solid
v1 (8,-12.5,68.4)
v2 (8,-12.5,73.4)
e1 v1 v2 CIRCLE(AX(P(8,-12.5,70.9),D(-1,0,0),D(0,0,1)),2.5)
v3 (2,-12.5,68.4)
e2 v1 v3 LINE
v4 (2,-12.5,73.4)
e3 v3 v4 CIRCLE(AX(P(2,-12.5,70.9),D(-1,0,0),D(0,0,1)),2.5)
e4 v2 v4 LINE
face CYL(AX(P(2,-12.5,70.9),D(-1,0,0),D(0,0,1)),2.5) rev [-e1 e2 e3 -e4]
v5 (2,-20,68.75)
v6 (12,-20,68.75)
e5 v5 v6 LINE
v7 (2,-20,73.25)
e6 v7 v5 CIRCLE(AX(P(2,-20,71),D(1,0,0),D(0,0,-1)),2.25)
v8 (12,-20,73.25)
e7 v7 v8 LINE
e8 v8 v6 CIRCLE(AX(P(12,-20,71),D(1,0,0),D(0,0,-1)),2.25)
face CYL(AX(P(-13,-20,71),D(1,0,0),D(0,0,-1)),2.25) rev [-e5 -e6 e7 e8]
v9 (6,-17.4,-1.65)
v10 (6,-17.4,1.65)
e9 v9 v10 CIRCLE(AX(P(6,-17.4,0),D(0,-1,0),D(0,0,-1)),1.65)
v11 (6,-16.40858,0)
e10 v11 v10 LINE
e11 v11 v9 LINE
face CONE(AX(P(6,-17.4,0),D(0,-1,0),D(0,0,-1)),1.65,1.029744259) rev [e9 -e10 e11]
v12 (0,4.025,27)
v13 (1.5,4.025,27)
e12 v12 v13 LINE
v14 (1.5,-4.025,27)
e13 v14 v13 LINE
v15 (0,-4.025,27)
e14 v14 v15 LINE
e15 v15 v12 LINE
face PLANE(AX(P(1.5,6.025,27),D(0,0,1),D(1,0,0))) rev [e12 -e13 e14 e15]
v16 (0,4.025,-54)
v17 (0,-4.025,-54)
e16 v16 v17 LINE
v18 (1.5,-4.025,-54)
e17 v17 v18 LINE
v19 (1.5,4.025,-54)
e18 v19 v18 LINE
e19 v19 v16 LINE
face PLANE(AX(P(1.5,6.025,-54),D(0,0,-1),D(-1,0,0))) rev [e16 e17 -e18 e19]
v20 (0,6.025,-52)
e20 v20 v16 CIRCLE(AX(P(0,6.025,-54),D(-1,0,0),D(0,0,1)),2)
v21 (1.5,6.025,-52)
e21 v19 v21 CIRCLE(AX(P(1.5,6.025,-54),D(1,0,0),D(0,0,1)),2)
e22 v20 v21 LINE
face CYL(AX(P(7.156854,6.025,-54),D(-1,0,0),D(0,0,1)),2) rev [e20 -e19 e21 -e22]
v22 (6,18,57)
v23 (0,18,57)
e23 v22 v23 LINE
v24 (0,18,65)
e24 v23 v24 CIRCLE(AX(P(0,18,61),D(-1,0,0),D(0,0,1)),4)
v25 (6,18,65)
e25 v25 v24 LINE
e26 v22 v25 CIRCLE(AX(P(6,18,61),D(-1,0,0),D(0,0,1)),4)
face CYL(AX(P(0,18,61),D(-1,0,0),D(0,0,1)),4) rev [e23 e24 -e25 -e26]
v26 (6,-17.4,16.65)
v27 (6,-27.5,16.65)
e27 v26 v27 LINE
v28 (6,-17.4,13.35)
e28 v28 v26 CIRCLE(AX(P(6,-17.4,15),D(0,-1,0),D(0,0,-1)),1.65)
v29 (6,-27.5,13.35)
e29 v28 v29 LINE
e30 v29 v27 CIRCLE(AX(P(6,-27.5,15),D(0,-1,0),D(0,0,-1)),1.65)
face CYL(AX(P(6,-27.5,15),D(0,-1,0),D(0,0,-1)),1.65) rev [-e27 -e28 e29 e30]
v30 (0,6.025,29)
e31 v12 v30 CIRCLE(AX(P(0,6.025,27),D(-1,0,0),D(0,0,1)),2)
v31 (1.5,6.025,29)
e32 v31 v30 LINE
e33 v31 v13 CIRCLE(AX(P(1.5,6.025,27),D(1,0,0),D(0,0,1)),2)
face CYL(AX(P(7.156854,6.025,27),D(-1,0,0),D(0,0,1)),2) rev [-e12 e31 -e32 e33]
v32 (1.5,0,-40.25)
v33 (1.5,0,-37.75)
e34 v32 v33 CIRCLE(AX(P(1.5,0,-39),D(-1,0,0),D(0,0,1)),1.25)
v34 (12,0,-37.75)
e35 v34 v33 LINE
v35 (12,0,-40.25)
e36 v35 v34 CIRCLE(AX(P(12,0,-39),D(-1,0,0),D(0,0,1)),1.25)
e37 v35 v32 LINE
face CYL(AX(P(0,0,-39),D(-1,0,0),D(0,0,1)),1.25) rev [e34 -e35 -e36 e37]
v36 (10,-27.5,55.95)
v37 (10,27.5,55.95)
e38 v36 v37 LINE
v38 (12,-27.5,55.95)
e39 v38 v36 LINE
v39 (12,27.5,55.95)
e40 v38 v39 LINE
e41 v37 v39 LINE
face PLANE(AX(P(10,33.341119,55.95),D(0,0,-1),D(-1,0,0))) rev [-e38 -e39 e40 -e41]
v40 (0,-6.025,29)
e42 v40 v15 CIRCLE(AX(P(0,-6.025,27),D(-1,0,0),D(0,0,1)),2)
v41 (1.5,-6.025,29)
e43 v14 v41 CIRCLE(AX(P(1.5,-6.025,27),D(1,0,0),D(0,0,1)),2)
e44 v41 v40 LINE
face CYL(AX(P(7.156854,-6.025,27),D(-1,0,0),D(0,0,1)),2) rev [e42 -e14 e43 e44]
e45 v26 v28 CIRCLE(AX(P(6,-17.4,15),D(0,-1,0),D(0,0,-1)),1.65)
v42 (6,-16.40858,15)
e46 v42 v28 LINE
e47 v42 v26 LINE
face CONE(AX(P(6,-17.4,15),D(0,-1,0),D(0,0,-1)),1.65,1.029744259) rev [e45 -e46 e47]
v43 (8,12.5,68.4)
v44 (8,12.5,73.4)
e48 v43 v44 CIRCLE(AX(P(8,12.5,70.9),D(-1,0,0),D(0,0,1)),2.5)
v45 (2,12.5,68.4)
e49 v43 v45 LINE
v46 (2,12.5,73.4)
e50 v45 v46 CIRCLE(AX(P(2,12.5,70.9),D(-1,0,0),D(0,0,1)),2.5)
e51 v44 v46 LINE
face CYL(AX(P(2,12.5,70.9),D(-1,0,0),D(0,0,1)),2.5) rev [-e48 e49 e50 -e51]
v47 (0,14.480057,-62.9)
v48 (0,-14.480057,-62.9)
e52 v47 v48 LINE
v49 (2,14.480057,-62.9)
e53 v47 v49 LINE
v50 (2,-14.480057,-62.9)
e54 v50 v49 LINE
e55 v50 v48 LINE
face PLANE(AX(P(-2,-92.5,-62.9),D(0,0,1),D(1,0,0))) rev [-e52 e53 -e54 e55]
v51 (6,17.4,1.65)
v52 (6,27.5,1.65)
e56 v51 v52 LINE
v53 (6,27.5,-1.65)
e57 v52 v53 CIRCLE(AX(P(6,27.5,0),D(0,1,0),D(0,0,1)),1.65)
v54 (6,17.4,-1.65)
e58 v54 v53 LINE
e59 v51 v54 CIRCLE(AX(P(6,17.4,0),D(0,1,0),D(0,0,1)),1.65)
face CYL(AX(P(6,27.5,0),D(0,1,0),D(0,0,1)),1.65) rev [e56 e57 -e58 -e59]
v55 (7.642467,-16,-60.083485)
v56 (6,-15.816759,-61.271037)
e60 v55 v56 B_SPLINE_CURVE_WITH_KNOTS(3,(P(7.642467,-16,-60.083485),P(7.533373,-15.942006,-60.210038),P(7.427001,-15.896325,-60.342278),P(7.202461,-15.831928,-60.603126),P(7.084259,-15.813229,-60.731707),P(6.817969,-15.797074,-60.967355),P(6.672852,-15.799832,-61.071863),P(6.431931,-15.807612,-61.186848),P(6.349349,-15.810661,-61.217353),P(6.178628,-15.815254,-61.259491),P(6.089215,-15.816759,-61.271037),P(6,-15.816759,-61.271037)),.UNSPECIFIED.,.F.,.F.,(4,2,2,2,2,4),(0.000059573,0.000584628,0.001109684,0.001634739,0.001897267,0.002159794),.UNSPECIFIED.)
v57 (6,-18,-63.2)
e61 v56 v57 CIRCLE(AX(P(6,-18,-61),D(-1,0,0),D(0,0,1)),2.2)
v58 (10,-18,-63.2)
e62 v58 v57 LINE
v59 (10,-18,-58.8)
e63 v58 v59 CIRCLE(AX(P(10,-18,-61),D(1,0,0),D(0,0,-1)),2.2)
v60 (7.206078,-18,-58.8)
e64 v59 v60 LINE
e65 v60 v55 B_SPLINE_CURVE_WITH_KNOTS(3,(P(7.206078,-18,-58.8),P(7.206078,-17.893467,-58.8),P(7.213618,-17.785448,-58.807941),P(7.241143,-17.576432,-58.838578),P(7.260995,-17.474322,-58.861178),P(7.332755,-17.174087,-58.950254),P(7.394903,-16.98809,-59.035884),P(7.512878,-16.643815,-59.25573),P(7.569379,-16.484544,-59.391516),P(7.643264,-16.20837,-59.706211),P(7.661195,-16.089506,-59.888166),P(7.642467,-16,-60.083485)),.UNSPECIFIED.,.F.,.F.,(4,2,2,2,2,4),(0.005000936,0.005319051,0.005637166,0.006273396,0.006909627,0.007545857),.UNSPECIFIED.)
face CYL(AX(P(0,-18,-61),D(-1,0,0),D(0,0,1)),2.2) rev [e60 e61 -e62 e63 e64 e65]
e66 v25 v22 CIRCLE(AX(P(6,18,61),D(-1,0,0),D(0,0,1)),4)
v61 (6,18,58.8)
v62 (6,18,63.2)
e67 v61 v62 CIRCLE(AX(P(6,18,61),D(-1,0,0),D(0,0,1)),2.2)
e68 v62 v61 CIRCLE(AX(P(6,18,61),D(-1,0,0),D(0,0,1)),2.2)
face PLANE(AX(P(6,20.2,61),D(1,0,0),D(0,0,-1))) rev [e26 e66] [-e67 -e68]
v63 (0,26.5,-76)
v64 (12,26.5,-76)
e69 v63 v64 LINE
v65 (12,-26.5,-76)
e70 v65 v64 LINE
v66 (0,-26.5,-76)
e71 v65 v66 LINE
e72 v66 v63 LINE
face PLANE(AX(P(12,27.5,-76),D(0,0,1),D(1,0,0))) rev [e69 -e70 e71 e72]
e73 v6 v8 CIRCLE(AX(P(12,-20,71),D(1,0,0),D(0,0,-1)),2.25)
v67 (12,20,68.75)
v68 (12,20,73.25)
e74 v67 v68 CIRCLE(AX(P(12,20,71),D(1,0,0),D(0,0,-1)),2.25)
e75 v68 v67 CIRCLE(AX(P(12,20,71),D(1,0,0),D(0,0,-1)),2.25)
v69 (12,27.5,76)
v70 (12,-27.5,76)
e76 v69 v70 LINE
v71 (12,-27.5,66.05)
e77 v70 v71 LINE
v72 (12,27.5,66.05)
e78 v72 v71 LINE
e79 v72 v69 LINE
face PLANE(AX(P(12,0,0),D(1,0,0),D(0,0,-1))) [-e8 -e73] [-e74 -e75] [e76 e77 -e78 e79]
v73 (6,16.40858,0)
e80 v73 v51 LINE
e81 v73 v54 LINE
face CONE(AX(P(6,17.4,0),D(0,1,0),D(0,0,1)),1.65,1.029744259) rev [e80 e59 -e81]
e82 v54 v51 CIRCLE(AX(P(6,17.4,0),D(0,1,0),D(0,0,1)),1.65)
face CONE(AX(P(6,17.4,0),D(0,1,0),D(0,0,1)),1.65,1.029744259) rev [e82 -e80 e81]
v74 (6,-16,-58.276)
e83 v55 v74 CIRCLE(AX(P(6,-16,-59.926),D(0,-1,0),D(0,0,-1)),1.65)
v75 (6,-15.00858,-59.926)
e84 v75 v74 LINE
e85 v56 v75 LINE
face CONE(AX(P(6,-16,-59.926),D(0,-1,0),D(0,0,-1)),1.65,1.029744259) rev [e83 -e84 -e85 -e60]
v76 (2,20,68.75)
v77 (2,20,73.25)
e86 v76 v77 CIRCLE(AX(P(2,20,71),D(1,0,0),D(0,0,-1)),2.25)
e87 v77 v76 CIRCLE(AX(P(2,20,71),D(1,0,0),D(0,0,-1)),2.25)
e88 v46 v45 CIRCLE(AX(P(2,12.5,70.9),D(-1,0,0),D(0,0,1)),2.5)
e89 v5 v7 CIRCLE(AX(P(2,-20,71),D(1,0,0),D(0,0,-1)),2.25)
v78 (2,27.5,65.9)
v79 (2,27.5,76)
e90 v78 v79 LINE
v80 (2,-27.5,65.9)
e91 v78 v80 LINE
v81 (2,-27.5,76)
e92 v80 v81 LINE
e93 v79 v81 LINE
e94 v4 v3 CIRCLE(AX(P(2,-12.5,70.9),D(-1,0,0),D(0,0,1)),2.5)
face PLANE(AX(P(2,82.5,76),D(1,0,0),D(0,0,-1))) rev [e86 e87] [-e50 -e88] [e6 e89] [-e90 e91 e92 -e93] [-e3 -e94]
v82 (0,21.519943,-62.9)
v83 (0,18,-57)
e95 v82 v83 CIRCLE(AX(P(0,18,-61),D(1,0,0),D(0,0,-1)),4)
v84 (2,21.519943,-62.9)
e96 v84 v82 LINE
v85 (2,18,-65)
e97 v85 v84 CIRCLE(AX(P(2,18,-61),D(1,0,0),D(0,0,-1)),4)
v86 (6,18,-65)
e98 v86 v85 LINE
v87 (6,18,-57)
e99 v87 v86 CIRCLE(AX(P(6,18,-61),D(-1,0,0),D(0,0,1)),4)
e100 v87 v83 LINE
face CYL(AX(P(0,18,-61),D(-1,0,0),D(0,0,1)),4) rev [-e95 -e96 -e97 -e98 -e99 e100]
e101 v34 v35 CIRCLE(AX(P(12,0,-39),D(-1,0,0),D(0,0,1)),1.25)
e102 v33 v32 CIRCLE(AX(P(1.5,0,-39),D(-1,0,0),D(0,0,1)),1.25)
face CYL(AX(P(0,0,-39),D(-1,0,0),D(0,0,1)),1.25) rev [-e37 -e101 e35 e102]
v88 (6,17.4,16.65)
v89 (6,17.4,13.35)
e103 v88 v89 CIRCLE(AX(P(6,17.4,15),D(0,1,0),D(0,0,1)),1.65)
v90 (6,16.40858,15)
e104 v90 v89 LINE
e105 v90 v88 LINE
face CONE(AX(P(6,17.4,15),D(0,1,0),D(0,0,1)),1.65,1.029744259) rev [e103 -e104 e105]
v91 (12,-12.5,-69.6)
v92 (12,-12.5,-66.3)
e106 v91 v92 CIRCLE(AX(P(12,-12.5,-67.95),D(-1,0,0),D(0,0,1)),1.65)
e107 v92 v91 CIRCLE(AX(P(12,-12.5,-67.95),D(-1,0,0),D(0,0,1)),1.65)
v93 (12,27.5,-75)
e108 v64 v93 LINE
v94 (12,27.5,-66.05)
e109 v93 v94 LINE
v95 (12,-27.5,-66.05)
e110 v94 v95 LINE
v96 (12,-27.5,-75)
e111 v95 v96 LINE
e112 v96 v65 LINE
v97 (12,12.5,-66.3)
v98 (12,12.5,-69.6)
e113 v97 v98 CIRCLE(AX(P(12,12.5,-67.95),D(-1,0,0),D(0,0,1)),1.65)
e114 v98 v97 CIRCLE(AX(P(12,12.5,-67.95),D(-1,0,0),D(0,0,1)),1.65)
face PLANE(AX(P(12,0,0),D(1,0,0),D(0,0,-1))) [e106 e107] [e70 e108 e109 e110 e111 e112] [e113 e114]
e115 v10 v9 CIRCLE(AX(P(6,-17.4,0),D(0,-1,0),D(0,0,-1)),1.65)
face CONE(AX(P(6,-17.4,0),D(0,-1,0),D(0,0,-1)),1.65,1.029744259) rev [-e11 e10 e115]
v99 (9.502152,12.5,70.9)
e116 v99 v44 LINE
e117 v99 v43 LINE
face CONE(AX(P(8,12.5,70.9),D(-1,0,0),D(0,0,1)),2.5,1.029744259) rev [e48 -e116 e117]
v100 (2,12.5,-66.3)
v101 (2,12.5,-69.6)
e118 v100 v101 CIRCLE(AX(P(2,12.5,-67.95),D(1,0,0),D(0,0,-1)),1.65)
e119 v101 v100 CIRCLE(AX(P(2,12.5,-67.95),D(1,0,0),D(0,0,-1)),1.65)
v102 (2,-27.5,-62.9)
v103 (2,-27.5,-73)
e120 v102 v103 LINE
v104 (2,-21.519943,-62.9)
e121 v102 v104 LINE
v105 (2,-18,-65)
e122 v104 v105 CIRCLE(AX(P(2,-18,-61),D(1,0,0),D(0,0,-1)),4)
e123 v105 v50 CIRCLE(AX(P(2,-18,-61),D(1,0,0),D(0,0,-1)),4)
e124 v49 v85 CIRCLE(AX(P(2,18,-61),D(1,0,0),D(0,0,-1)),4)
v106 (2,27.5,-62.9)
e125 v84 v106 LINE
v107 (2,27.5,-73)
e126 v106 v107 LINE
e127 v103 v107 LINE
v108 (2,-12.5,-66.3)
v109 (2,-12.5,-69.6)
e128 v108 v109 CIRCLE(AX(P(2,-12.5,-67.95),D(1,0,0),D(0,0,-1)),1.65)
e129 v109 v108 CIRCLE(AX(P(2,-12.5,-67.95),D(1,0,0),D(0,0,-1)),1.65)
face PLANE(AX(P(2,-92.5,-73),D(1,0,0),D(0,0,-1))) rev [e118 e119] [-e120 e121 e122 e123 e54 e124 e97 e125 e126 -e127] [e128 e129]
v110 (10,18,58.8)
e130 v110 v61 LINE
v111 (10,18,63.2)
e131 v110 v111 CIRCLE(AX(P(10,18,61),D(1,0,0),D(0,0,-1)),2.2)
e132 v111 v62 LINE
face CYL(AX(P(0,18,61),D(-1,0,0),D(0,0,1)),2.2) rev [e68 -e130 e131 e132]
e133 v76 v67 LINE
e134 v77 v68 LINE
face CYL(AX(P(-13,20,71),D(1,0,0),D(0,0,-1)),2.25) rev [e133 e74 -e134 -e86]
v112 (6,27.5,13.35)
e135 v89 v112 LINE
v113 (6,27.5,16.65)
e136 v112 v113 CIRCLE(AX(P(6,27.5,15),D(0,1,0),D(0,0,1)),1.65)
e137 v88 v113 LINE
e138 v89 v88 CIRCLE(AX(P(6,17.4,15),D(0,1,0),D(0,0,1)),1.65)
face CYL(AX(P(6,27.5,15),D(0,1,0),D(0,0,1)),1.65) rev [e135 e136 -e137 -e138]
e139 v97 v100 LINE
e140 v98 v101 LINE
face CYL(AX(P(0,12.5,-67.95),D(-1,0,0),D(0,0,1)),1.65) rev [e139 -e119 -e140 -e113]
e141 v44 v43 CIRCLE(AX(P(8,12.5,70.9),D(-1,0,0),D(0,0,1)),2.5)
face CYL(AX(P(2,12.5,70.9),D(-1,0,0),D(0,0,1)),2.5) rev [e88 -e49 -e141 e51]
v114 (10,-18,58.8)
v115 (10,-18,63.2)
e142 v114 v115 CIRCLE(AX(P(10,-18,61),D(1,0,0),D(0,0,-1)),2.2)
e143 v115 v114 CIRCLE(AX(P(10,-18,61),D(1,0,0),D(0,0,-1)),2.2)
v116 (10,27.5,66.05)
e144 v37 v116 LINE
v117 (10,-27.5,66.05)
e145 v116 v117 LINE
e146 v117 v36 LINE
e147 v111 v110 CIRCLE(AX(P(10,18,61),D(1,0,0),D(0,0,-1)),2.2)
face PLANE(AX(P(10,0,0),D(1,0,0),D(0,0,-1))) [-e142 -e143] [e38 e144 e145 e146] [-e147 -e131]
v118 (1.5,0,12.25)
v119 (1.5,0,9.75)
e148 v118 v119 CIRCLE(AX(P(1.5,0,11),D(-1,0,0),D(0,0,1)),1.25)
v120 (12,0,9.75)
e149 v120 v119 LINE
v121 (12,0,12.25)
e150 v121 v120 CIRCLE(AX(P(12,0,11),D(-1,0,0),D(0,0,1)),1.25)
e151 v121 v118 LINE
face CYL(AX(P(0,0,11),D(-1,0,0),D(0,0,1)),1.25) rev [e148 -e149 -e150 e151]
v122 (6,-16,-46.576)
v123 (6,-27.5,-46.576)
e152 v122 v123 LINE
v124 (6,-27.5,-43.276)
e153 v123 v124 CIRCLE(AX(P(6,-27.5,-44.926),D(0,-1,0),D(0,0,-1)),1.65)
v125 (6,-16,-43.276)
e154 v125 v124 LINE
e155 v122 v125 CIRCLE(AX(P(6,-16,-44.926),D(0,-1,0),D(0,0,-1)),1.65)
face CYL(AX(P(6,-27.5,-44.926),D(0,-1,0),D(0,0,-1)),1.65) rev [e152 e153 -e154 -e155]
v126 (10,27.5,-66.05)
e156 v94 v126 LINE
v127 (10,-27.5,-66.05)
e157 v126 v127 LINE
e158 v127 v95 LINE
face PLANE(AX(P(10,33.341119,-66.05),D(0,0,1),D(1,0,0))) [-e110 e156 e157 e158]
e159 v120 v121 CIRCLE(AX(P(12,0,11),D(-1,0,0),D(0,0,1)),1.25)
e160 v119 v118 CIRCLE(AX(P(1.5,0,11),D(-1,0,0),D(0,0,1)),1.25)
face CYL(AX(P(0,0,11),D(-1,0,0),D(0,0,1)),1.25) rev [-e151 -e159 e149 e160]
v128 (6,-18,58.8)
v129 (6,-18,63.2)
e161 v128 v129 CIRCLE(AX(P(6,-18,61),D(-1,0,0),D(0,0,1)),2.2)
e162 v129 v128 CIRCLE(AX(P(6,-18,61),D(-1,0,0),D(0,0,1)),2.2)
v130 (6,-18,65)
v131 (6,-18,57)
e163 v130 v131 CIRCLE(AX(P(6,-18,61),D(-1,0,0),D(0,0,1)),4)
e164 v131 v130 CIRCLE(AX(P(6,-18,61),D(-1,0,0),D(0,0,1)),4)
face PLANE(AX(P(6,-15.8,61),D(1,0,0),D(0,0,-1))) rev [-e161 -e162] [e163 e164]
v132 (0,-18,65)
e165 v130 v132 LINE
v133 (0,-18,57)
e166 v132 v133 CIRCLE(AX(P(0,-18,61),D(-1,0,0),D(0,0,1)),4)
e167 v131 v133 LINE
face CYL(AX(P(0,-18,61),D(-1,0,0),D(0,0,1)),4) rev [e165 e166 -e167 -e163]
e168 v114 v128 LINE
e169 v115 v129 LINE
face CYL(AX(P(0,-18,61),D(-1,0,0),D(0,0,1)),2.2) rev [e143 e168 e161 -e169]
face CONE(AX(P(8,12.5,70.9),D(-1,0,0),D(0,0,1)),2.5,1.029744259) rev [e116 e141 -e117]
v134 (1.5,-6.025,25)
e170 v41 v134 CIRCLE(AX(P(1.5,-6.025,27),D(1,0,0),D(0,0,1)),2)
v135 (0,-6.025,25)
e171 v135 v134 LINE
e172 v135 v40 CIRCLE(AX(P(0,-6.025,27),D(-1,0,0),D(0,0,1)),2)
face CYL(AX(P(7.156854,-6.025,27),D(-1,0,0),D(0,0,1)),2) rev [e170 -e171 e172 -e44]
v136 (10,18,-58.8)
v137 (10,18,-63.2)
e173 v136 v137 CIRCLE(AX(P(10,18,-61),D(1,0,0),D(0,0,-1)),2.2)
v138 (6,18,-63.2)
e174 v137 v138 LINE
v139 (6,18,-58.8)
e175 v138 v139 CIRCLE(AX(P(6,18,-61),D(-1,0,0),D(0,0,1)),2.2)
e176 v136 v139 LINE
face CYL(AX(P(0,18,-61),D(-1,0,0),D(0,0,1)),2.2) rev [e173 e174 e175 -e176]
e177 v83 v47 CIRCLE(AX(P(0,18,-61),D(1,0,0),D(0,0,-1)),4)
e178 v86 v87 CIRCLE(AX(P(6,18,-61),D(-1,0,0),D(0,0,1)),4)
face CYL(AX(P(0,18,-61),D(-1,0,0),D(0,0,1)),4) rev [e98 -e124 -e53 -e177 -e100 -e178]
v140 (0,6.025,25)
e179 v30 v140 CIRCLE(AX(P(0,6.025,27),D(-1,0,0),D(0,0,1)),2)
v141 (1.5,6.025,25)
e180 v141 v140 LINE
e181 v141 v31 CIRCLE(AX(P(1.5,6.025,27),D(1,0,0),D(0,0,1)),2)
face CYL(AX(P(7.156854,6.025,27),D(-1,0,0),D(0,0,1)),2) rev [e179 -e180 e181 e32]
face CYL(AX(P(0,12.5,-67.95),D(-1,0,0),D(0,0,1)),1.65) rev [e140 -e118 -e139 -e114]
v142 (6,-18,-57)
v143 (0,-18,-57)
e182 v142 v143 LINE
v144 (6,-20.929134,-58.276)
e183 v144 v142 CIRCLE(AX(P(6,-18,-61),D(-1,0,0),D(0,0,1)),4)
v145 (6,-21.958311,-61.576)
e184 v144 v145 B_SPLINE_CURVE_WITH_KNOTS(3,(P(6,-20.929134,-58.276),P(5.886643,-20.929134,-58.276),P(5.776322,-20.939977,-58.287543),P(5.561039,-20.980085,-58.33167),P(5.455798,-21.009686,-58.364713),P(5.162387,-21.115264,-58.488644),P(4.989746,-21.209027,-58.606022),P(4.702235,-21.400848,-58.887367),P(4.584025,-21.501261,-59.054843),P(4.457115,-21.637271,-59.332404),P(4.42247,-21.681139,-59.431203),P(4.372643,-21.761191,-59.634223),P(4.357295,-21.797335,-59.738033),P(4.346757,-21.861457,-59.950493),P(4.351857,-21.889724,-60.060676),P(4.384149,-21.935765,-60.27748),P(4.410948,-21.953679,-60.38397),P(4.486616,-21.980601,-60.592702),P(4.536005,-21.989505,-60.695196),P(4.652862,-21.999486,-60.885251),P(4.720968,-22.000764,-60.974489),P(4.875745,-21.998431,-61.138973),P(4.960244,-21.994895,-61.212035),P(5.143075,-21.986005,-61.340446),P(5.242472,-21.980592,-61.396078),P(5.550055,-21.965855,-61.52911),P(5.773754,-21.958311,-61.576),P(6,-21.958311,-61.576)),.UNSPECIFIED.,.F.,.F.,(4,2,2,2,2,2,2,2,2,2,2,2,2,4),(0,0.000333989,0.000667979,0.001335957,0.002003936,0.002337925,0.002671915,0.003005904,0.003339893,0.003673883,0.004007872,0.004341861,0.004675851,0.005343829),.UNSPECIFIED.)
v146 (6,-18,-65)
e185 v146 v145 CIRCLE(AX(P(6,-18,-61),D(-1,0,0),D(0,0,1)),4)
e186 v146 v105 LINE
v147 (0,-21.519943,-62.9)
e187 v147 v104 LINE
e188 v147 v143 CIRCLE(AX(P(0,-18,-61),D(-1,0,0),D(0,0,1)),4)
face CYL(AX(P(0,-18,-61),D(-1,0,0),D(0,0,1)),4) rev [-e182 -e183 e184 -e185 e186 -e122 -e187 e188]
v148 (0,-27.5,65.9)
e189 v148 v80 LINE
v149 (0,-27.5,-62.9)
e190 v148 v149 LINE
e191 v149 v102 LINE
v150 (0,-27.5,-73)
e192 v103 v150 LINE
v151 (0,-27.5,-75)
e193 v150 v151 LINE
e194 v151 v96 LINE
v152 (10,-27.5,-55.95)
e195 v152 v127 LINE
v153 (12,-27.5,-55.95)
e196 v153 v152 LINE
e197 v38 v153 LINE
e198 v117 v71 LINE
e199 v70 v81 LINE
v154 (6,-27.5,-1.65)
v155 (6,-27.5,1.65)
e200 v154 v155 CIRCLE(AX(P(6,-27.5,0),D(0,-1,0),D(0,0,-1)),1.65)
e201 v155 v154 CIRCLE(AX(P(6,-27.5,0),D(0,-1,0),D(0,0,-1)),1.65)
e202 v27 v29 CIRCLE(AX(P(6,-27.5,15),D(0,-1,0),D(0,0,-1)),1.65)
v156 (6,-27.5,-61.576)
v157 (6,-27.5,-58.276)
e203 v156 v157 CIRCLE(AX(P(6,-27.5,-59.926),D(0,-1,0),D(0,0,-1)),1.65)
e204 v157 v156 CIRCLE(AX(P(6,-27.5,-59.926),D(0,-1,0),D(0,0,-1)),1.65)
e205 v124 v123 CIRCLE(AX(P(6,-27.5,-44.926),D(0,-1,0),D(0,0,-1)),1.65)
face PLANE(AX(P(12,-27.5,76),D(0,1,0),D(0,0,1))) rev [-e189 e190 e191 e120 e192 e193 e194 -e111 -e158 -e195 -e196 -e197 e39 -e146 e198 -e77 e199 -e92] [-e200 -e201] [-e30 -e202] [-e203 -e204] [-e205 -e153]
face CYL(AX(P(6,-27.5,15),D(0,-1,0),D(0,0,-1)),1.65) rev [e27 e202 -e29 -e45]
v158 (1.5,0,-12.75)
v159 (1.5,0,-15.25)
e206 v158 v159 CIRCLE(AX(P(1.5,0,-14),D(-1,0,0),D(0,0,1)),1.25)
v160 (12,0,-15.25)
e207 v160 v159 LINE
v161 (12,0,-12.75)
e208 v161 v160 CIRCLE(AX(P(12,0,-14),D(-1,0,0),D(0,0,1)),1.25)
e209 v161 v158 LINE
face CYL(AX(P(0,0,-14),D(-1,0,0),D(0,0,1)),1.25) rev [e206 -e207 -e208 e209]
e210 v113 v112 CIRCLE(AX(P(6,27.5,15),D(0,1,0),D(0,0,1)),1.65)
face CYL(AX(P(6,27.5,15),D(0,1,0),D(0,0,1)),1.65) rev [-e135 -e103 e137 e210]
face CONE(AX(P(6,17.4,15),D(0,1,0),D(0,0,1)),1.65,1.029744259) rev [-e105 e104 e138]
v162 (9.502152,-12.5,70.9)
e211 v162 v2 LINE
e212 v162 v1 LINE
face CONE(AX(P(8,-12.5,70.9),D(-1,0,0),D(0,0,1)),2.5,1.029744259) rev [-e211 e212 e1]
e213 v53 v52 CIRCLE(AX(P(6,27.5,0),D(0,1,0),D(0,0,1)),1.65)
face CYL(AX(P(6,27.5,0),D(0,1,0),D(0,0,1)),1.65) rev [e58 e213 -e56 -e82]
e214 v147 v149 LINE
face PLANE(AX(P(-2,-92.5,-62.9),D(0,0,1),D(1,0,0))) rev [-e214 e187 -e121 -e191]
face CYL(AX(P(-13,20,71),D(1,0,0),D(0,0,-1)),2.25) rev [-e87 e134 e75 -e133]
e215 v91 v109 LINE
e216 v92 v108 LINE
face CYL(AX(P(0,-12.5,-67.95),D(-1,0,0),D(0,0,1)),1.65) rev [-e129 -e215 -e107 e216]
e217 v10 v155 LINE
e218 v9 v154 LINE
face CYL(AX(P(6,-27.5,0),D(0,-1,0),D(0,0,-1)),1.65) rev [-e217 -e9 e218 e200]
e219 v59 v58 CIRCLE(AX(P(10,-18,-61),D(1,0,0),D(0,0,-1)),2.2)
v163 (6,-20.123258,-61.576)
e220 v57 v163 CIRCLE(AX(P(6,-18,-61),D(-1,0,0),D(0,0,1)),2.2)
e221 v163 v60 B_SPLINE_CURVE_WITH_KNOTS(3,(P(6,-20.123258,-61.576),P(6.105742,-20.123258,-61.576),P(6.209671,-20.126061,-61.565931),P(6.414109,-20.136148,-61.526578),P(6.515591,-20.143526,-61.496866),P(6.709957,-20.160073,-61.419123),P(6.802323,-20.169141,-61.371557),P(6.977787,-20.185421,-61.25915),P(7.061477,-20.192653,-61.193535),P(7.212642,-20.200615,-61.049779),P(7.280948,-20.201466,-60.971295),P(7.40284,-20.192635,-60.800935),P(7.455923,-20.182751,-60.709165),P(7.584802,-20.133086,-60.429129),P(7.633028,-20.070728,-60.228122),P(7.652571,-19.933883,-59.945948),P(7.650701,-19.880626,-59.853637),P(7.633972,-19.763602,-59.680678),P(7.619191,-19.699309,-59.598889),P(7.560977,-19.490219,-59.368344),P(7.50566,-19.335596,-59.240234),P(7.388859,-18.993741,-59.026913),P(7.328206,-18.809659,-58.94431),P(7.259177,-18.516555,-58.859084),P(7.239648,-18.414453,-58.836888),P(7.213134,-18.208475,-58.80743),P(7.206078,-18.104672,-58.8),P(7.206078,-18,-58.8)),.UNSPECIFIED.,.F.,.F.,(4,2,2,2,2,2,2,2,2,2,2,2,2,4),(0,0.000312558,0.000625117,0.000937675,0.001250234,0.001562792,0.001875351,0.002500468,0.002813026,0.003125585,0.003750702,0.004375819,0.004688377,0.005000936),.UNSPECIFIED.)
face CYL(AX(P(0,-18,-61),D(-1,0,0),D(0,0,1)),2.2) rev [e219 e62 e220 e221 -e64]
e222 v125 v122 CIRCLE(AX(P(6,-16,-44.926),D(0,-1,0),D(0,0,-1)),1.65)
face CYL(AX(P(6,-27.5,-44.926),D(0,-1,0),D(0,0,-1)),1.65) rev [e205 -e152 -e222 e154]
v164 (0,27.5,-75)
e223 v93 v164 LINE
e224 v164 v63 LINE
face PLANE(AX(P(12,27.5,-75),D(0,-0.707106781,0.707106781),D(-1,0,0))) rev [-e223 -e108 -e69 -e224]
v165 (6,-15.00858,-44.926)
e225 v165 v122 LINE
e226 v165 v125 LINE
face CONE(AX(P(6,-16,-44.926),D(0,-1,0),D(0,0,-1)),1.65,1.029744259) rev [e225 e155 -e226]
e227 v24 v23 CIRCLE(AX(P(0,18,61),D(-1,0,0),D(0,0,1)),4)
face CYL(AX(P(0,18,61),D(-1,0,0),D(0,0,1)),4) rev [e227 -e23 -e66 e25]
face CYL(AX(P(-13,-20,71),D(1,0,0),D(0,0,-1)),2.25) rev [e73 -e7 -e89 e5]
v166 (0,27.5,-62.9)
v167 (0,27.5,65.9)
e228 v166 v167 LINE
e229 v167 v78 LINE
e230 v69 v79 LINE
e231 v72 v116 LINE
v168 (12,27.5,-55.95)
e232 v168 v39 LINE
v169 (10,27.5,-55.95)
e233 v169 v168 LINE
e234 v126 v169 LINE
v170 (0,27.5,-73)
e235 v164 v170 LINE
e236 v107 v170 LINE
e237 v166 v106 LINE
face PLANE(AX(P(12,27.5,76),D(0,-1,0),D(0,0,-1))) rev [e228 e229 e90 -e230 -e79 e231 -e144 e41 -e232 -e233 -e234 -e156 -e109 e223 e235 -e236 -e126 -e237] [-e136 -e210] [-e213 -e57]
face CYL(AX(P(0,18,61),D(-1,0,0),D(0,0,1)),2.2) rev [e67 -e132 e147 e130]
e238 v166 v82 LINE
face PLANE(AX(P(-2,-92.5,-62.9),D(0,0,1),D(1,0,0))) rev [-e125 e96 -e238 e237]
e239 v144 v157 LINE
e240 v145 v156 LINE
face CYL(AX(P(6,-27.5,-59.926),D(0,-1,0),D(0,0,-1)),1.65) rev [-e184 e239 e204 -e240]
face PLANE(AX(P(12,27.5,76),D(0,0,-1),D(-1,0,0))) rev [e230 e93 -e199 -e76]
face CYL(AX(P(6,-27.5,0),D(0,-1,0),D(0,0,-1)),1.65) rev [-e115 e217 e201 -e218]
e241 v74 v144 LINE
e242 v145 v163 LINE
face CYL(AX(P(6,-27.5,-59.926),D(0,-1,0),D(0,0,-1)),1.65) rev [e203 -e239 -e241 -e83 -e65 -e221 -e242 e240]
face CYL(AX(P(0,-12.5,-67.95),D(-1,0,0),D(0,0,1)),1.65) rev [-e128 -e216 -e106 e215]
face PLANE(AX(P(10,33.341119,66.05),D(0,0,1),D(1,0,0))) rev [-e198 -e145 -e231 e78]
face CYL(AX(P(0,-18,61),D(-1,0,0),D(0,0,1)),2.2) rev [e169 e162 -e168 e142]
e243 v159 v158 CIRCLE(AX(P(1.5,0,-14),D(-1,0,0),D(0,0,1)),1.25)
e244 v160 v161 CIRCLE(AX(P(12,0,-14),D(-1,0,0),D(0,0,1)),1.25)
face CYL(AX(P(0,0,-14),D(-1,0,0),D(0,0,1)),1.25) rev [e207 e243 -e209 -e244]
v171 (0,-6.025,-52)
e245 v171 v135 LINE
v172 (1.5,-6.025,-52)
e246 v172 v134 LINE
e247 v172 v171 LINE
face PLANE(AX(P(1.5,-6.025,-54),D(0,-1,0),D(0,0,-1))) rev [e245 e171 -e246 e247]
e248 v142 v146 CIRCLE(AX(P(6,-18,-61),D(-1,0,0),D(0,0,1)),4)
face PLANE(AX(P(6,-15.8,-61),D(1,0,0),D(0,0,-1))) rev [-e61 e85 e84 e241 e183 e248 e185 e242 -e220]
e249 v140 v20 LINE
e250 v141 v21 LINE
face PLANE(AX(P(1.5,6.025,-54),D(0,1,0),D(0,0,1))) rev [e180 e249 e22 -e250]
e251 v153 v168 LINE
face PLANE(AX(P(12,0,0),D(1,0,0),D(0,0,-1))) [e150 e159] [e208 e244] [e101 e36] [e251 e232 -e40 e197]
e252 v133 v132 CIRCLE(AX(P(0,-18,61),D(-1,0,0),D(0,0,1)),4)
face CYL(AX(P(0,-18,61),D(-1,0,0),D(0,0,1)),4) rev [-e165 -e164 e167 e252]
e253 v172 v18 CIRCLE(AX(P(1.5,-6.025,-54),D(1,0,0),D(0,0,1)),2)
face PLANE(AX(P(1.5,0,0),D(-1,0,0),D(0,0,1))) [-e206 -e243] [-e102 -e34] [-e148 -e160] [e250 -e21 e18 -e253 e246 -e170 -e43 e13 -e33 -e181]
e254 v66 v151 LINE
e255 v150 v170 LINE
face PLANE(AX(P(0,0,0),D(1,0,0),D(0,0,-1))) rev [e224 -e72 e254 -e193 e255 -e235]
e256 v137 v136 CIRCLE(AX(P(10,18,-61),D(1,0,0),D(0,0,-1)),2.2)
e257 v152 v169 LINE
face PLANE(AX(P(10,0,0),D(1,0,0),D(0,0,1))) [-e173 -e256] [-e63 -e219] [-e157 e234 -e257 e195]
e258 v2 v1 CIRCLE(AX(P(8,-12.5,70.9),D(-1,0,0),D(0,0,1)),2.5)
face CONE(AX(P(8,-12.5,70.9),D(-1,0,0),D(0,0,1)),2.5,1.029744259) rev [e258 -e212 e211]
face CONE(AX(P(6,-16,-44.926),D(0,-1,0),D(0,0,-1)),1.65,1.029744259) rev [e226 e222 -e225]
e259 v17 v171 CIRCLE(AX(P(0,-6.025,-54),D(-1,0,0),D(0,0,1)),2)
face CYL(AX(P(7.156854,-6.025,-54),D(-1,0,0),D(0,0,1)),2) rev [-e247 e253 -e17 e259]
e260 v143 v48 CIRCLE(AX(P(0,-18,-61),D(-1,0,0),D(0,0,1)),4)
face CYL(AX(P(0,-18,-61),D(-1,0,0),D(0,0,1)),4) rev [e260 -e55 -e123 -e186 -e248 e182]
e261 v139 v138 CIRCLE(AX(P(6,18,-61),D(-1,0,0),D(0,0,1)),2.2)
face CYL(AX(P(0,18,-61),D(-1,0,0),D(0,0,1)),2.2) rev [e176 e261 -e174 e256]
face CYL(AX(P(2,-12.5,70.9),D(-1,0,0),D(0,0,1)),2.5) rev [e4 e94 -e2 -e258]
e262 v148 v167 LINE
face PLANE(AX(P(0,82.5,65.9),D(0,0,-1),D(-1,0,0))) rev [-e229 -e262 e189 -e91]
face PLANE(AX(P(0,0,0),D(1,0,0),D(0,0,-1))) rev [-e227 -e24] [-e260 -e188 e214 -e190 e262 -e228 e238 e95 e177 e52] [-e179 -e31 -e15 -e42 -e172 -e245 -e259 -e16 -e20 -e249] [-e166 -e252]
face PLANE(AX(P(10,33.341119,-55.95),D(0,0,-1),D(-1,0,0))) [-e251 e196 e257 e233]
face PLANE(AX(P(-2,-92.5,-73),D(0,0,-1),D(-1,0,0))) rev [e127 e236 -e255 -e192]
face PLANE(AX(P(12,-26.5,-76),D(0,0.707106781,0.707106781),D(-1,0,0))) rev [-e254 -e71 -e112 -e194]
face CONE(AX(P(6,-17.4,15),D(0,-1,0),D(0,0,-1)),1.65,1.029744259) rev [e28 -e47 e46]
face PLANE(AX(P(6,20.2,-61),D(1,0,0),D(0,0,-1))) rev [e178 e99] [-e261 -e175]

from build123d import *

# Parameters (mm, degrees)
SKETCH_1_W                  = 152
SKETCH_1_H                  = 55
EXTRUDE_1_DEPTH             = 12
SKETCH_2_W                  = 10.1
SKETCH_2_H                  = 67.741828953
CUT_EXTRUDE_1_DEPTH         = 2
SKETCH_3_W                  = 81
SKETCH_3_H                  = 12.05
CUT_EXTRUDE_2_DEPTH         = 1.5
SKETCH_4_R                  = 2
CUT_EXTRUDE_3_DEPTH         = 1.5
SKETCH_5_W                  = 2
SKETCH_5_H                  = 10.1
CUT_EXTRUDE_4_DEPTH         = 110
SKETCH_7_W                  = 4
SKETCH_7_H                  = 10.1
CUT_EXTRUDE_5_DEPTH         = 120
CHAMFER_1_SIZE              = 1
HOLE_WIZARD_M4_1_AT_2_COUNT = 2
HOLE_WIZARD_M4_1_AT_2_PITCH = 15
HOLE_WIZARD_5_0_5_2_D       = 5
HOLE_WIZARD_5_0_5_2_DEPTH   = 6
HOLE_WIZARD_5_0_5_2_TIP     = 1.502151548
HOLE_WIZARD_1_D             = 4.4
HOLE_WIZARD_1_CBORE_D       = 8
HOLE_WIZARD_1_CBORE_DEPTH   = 6
HOLE_WIZARD_M3_1_D          = 2.5
HOLE_WIZARD_M4_2_D          = 3.3
HOLE_WIZARD_M4_2_DEPTH      = 11.5
HOLE_WIZARD_M4_2_TIP        = 0.991420021
HOLE_WIZARD_M4_3_D          = 3.3
SKETCH_30_R                 = 2.25
CUT_EXTRUDE_6_DEPTH         = 25


with BuildPart() as part:
    # 草图1 → 凸台-拉伸1 (new body)
    with BuildSketch(Plane(origin=(0, 0, 0), x_dir=(0, 0, -1), z_dir=(1, 0, 0))):
        Rectangle(SKETCH_1_W, SKETCH_1_H)
    extrude(amount=EXTRUDE_1_DEPTH)

    # 草图2 → 切除-拉伸1 (cut)
    with BuildSketch(Plane(origin=(12, 0, 0), x_dir=(0, 0, -1), z_dir=(1, 0, 0))):
        with Locations((-61, -0.529795054)):
            Rectangle(SKETCH_2_W, SKETCH_2_H)
    cut_extrude_1 = extrude(amount=-CUT_EXTRUDE_1_DEPTH, mode=Mode.SUBTRACT)

    # 草图3 → 切除-拉伸2 (cut)
    with BuildSketch(Plane.ZY):
        with Locations((-13.5, 0)):
            Rectangle(SKETCH_3_W, SKETCH_3_H)
    extrude(amount=-CUT_EXTRUDE_2_DEPTH, mode=Mode.SUBTRACT)

    # 草图4 → 切除-拉伸3 (cut)
    with BuildSketch(Plane.ZY):
        with Locations((-54, 6.025)):
            Circle(SKETCH_4_R)
        with Locations((-54, -6.025)):
            Circle(SKETCH_4_R)
        with Locations((27, -6.025)):
            Circle(SKETCH_4_R)
        with Locations((27, 6.025)):
            Circle(SKETCH_4_R)
    extrude(amount=-CUT_EXTRUDE_3_DEPTH, mode=Mode.SUBTRACT)

    # 草图5 → 切除-拉伸4 (cut)
    with BuildSketch(Plane.XZ.offset(27.5)):
        with Locations((1, 70.95)):
            Rectangle(SKETCH_5_W, SKETCH_5_H)
    extrude(amount=-CUT_EXTRUDE_4_DEPTH, mode=Mode.SUBTRACT)

    # 草图7 → 切除-拉伸5 (cut)
    with BuildSketch(Plane(origin=(0, 27.5, 0), x_dir=(1, 0, 0), z_dir=(0, 1, 0))):
        with Locations((0, 67.95)):
            Rectangle(SKETCH_7_W, SKETCH_7_H)
    extrude(amount=-CUT_EXTRUDE_5_DEPTH, mode=Mode.SUBTRACT)

    # 倒角1
    chamfer_1_edges = [part.edges().sort_by_distance(p)[0] for p in [
        (6, -27.5, -76),
        (6, 27.5, -76),
    ]]
    chamfer(chamfer_1_edges, length=CHAMFER_1_SIZE)

    # 草图9 → M4 螺纹孔1 (revolve, cut)
    with BuildSketch(Plane(origin=(6, 27.5, 15), x_dir=(0, 0, 1), z_dir=(1, 0, 0))):
        Polygon((0, 0), (0, 11.091420021), (1.65, 10.1), (1.65, 0), align=None)
    hole_wizard_m4_1 = revolve(axis=Axis((6, 33.85, 15), (0, -1, 0)), mode=Mode.SUBTRACT)

    # M4 螺纹孔1 at 2: M4 螺纹孔1 ×2
    with Locations(*[(0, 0, -i * HOLE_WIZARD_M4_1_AT_2_PITCH) for i in range(1, HOLE_WIZARD_M4_1_AT_2_COUNT)]):
        add(hole_wizard_m4_1, mode=Mode.SUBTRACT)

    # 镜向1: M4 螺纹孔1 across plane
    add(hole_wizard_m4_1.mirror(Plane.ZX), mode=Mode.SUBTRACT)

    # 镜向1 copy 1 sketch → 镜向1 copy 1 (revolve, cut)
    with BuildSketch(Plane(origin=(6, -27.5, 0), x_dir=(0, 0, 1), z_dir=(1, 0, 0))):
        Polygon((0, 0), (0, -11.091420021), (1.65, -10.1), (1.65, 0), align=None)
    revolve(axis=Axis((6, -33.85, 0), (0, -1, 0)), mode=Mode.SUBTRACT)

    # Ø5.0 (5) 直径孔2
    with Locations(Plane.ZY.offset(-2)):
        with Locations((70.9, 12.5), (70.9, -12.5)):
            Hole(HOLE_WIZARD_5_0_5_2_D / 2, depth=HOLE_WIZARD_5_0_5_2_DEPTH)
            with Locations((0, 0, -(HOLE_WIZARD_5_0_5_2_DEPTH + HOLE_WIZARD_5_0_5_2_TIP / 2))):  # 118° drill point
                Cone(0, HOLE_WIZARD_5_0_5_2_D / 2, HOLE_WIZARD_5_0_5_2_TIP, mode=Mode.SUBTRACT)

    # 镜向2: 切除-拉伸1 across plane
    add(cut_extrude_1.mirror(Plane.XY), mode=Mode.SUBTRACT)

    # 打孔尺寸(%根据)内六角圆柱头螺钉的类型1 (through all)
    with Locations(Plane.ZY):
        with Locations((61, -18), (61, 18), (-61, 18), (-61, -18)):
            CounterBoreHole(HOLE_WIZARD_1_D / 2, HOLE_WIZARD_1_CBORE_D / 2, HOLE_WIZARD_1_CBORE_DEPTH)

    # M3 螺纹孔1 (through all)
    with Locations(Plane.ZY):
        with Locations((11, 0), (-14, 0), (-39, 0)):
            Hole(HOLE_WIZARD_M3_1_D / 2)

    # M4 螺纹孔2
    with Locations(Plane(origin=(0, -27.5, 0), x_dir=(-1, 0, 0), z_dir=(0, -1, 0))):
        with Locations((-6, 44.926), (-6, 59.926)):
            Hole(HOLE_WIZARD_M4_2_D / 2, depth=HOLE_WIZARD_M4_2_DEPTH)
            with Locations((0, 0, -(HOLE_WIZARD_M4_2_DEPTH + HOLE_WIZARD_M4_2_TIP / 2))):  # 118° drill point
                Cone(0, HOLE_WIZARD_M4_2_D / 2, HOLE_WIZARD_M4_2_TIP, mode=Mode.SUBTRACT)

    # M4 螺纹孔3 (through all)
    with Locations(Plane.ZY):
        with Locations((-67.95, 12.5), (-67.95, -12.5)):
            Hole(HOLE_WIZARD_M4_3_D / 2)

    # 草图30 → 切除-拉伸6 (cut)
    with BuildSketch(Plane(origin=(12, 0, 0), x_dir=(0, 0, -1), z_dir=(1, 0, 0))):
        with Locations((-71, 20)):
            Circle(SKETCH_30_R)
        with Locations((-71, -20)):
            Circle(SKETCH_30_R)
    extrude(amount=-CUT_EXTRUDE_6_DEPTH, mode=Mode.SUBTRACT)


solid = part.part
